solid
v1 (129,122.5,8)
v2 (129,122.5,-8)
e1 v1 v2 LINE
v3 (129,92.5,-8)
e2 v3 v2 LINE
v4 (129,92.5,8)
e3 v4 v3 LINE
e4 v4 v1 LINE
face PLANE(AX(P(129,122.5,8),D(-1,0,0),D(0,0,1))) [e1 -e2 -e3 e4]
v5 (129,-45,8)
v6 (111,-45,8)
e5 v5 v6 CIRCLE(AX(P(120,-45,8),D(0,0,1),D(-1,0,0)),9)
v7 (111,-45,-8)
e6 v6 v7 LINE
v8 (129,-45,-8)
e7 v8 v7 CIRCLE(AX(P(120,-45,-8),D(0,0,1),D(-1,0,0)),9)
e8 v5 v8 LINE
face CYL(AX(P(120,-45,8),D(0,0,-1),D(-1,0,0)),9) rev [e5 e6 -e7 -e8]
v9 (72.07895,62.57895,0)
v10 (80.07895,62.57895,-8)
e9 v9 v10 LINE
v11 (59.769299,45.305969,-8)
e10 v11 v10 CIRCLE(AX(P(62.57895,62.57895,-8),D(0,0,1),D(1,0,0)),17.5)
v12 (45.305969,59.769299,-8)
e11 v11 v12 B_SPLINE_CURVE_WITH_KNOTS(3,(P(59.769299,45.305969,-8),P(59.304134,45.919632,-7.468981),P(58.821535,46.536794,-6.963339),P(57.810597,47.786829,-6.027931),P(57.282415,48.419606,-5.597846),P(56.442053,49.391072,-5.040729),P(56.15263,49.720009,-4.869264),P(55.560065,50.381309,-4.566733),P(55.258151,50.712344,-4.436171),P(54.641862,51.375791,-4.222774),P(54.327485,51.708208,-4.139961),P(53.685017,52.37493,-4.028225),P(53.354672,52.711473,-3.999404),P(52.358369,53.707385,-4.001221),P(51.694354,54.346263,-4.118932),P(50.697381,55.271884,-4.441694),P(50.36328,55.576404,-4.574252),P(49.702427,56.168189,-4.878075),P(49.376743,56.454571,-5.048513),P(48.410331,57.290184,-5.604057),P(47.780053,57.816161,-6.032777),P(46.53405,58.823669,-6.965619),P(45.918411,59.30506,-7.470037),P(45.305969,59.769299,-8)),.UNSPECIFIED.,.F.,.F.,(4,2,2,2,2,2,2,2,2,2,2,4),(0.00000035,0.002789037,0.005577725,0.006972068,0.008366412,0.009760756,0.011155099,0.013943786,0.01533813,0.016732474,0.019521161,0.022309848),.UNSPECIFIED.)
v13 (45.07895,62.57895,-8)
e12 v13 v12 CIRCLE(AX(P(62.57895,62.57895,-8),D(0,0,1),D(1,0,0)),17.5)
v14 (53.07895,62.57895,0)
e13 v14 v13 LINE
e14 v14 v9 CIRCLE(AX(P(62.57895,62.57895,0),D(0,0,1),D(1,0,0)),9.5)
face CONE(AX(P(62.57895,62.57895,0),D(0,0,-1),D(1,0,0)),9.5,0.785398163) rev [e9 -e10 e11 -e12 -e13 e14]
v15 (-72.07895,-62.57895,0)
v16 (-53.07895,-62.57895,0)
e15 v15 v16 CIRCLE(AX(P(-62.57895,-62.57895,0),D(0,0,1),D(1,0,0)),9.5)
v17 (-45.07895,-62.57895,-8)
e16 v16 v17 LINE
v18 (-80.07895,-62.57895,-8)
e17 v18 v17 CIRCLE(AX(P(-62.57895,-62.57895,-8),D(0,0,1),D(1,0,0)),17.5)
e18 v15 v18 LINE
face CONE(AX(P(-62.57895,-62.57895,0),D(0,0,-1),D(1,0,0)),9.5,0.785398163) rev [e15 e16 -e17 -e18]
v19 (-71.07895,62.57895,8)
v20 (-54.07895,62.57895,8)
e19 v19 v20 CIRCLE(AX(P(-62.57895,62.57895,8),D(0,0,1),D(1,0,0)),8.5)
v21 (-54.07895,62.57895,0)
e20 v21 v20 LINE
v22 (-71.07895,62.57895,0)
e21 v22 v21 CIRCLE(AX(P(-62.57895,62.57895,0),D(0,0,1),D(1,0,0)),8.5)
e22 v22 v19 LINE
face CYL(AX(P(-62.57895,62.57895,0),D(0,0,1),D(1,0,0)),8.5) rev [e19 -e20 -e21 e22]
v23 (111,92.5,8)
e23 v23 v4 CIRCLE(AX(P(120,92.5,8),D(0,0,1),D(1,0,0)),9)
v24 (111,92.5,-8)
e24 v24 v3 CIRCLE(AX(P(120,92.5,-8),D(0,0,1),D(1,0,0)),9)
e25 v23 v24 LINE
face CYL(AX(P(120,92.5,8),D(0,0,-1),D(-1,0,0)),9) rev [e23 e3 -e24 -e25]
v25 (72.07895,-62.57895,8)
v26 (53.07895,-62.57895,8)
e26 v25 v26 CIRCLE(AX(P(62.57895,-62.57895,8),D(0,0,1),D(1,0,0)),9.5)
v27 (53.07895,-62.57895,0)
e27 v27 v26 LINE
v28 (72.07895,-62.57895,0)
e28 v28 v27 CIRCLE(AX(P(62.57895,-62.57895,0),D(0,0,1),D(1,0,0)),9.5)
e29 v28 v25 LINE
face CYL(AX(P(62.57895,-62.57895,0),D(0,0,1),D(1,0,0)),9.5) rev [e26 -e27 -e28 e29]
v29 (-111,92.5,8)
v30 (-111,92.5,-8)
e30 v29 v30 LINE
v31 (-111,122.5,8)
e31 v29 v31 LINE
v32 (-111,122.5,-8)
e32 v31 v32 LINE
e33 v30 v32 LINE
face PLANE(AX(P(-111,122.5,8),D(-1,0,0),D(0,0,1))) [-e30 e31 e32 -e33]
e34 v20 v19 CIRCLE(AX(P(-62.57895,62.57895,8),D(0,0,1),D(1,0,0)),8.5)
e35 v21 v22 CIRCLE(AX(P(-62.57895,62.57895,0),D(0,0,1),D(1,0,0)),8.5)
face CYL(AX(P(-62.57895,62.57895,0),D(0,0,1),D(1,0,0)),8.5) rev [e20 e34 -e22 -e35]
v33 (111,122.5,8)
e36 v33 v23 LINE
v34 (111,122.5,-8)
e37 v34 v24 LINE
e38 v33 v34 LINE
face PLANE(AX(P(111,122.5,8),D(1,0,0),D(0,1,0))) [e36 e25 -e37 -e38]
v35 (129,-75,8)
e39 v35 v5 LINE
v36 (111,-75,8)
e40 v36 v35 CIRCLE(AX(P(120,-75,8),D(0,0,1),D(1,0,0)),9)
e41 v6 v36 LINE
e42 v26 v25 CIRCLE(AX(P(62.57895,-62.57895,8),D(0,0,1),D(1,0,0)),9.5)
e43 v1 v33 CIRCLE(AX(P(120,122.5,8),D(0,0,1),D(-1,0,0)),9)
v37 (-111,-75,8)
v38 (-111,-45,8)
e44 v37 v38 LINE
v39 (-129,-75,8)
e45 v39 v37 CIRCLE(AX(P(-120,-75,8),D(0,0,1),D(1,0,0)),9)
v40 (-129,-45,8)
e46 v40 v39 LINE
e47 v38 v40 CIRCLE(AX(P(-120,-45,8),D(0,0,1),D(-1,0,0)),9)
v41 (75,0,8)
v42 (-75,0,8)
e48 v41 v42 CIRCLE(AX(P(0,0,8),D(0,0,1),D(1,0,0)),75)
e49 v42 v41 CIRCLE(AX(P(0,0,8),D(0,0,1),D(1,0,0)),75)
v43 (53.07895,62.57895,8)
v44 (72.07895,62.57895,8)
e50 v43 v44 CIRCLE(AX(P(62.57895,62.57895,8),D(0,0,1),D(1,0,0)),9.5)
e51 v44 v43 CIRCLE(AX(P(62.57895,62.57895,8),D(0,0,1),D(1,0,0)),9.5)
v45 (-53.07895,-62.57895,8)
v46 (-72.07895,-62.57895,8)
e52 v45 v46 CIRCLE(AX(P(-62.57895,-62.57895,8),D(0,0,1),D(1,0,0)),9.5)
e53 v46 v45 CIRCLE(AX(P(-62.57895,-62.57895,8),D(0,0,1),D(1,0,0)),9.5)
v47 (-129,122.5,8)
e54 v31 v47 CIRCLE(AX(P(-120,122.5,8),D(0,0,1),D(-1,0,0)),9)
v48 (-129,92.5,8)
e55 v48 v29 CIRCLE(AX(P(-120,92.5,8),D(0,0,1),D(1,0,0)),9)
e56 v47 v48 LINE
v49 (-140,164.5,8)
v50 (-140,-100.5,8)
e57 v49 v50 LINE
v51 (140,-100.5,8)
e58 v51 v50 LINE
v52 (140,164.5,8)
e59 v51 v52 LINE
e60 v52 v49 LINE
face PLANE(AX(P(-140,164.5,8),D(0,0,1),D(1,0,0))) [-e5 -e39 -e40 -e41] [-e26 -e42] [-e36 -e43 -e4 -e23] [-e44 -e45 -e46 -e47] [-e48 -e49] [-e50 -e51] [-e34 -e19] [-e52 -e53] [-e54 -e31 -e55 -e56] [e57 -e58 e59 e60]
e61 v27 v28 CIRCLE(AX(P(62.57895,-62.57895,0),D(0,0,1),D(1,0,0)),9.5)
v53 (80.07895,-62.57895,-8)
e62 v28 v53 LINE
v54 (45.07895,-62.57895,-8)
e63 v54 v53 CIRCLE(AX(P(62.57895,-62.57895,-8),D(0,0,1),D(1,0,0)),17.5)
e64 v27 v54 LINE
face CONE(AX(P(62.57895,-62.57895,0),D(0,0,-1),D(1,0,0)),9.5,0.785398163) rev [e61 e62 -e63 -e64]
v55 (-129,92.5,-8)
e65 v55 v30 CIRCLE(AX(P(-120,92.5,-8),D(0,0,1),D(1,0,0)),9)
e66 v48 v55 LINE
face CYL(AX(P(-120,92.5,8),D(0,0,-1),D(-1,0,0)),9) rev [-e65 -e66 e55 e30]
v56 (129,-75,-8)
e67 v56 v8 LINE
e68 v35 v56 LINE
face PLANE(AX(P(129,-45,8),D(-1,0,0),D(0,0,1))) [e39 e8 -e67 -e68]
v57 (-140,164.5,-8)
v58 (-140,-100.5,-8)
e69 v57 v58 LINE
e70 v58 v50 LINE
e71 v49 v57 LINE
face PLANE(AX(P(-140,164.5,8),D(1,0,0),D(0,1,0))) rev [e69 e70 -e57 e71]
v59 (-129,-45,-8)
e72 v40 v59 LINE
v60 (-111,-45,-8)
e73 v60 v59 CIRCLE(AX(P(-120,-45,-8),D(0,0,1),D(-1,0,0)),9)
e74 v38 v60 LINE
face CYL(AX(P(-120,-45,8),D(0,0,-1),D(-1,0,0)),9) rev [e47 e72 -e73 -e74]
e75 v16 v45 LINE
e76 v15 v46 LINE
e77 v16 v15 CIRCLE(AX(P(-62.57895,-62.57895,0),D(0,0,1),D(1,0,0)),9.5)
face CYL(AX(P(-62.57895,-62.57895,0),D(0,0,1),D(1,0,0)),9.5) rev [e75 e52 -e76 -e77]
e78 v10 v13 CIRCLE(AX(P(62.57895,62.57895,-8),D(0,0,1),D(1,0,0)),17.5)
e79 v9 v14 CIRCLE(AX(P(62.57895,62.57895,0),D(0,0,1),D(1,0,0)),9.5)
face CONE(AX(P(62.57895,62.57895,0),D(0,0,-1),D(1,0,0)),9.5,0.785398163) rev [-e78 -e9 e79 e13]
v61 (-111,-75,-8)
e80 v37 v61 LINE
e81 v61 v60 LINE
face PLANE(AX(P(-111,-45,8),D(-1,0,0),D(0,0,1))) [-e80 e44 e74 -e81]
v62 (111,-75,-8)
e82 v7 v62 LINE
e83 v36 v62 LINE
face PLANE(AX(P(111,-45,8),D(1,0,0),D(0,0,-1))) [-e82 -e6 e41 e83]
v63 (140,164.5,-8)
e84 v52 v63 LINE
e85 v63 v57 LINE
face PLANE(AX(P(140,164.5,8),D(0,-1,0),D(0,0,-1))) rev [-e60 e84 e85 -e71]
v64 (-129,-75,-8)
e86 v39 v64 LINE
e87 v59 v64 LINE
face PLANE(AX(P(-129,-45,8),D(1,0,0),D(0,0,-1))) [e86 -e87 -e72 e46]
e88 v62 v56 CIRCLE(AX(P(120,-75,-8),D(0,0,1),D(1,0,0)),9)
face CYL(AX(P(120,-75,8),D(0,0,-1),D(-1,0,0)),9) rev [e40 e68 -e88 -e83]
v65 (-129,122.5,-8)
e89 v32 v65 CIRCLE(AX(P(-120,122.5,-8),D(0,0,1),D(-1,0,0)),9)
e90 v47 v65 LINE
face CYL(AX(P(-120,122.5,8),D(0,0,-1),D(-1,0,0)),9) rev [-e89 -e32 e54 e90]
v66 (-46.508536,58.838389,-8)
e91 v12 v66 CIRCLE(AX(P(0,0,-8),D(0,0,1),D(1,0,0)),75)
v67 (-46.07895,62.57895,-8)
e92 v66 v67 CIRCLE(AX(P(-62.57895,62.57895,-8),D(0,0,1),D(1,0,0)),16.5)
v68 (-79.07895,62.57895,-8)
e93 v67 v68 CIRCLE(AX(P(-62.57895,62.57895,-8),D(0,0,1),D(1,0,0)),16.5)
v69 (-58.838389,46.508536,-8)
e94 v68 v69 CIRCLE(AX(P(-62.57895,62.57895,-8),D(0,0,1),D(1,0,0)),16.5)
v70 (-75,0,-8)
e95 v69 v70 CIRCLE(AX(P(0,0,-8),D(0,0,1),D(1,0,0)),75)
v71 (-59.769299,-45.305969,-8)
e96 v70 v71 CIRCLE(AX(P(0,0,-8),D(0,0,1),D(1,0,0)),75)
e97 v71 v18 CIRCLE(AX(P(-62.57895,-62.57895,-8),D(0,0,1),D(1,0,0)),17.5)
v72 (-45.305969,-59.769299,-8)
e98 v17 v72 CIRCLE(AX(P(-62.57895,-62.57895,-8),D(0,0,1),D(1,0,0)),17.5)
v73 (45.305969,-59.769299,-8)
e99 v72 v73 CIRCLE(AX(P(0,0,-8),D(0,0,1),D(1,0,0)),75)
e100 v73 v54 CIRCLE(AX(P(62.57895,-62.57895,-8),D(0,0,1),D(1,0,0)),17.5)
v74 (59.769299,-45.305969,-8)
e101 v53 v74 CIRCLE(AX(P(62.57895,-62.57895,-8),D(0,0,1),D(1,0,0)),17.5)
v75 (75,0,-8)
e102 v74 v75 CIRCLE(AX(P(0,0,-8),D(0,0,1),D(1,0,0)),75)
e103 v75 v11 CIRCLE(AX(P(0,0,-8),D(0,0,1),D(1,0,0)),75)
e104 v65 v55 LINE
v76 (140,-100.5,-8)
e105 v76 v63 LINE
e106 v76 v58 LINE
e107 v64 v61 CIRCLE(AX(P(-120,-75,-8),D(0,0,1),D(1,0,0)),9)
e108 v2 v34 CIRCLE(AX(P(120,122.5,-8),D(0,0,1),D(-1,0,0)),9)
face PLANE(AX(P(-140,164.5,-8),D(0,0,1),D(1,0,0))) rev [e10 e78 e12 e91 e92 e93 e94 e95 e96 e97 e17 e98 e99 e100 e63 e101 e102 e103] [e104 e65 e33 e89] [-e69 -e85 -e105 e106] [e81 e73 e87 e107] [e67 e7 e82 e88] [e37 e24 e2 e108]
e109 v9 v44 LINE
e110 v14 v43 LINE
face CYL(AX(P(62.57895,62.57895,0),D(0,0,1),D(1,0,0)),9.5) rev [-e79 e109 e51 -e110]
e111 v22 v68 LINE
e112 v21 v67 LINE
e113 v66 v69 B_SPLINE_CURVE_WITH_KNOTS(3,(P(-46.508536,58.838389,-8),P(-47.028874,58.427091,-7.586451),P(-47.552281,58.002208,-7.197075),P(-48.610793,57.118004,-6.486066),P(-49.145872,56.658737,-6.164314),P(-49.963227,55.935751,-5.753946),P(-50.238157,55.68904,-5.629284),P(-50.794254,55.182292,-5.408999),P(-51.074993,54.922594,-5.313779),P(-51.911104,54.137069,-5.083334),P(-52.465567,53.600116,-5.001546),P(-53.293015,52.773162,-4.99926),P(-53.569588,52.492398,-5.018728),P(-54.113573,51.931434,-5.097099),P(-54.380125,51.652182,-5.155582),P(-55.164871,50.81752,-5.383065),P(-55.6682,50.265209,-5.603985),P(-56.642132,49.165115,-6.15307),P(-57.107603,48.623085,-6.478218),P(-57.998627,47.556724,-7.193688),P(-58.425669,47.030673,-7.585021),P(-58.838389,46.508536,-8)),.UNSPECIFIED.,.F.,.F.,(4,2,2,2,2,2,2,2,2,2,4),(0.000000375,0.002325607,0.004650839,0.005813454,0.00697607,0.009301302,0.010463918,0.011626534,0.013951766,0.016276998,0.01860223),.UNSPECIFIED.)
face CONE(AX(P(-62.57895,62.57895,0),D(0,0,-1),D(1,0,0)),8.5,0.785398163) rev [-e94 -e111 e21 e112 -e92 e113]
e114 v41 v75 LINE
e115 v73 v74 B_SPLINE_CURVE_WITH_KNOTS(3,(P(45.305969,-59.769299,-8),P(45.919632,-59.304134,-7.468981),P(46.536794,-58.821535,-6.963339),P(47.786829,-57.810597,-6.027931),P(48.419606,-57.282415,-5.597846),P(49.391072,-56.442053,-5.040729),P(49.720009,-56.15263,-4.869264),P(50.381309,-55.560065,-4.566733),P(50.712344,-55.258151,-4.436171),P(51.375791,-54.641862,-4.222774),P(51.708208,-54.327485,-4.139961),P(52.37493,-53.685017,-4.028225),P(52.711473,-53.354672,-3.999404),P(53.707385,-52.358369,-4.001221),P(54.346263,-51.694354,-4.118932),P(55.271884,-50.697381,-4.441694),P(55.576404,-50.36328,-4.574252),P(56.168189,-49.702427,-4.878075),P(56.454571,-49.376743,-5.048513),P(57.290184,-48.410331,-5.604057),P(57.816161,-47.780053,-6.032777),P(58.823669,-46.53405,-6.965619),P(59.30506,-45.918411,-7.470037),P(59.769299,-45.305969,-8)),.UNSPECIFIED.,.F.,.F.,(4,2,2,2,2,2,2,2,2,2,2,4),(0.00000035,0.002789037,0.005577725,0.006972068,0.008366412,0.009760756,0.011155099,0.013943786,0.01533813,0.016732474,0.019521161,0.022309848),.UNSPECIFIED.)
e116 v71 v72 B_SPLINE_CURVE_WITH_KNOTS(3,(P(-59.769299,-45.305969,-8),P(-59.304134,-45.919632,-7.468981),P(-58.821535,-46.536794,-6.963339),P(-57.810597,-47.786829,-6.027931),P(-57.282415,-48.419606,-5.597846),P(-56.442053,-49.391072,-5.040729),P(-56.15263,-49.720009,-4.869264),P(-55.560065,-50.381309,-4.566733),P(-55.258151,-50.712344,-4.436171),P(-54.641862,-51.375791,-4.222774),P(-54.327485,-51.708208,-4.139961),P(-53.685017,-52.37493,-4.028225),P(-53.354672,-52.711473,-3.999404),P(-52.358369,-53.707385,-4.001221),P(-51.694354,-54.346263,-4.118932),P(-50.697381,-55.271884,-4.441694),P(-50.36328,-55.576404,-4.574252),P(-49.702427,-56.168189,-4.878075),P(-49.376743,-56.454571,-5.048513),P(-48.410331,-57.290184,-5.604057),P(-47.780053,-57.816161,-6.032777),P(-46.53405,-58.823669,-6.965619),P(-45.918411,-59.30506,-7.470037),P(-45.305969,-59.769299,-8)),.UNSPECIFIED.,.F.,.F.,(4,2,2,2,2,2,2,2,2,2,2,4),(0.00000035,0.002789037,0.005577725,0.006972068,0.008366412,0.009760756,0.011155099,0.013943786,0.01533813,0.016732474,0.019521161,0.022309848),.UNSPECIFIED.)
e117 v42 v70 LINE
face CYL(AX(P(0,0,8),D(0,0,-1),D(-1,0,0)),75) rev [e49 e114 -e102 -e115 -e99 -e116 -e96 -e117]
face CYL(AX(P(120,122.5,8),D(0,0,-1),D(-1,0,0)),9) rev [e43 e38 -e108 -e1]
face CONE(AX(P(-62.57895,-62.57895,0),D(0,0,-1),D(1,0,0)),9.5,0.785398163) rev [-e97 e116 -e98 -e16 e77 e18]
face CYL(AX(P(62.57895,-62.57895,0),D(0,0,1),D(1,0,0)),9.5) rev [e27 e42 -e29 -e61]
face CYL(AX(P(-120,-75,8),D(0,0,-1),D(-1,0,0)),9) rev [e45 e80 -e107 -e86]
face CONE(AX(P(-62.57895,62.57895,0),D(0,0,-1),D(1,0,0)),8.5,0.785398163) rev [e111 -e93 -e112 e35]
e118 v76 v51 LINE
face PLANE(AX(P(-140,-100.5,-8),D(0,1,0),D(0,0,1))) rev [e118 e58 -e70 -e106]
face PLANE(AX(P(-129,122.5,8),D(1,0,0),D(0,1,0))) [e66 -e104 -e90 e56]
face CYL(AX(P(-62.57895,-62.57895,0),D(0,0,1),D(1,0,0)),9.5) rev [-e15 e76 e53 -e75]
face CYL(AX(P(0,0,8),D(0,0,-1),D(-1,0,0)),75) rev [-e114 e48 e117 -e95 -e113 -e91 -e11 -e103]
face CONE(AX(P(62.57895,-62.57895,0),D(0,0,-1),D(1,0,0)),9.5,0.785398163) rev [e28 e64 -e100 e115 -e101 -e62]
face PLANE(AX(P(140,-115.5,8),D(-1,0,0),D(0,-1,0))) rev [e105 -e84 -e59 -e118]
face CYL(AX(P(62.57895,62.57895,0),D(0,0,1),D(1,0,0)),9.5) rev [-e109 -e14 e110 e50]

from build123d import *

# Parameters (mm, degrees)
SKETCH1_W                = 280
SKETCH1_H                = 280
SKETCH1_R                = 75
EXTRUDE1_DEPTH           = 8
SKETCH_2_2_R             = 8.5
SKETCH_2_2_R_2           = 9.5
EXTRUDE2_DEPTH           = 8
EXTRUDE4_START           = -8
SKETCH_2_2_2_R           = 8.5
EXTRUDE4_DEPTH           = 8
EXTRUDE4_DRAFT           = 45
SKETCH_2_2_2_R_2         = 9.5
EXTRUDE4_PROFILE_2_DEPTH = 8
EXTRUDE4_PROFILE_2_DRAFT = 45
EXTRUDE4_PROFILE_3_DEPTH = 8
EXTRUDE4_PROFILE_3_DRAFT = 45
EXTRUDE4_PROFILE_4_DEPTH = 8
EXTRUDE4_PROFILE_4_DRAFT = 45
SKETCH3_W                = 280
SKETCH3_H                = 15
EXTRUDE5_DEPTH           = 16


with BuildPart() as part:
    # Sketch1 → Extrude1 (new, symmetric)
    with BuildSketch(Plane.XY):
        with Locations((0, 24.5)):
            Rectangle(SKETCH1_W, SKETCH1_H)
        Circle(SKETCH1_R, mode=Mode.SUBTRACT)
        with BuildLine():
            Line((-129, 122.5), (-129, 92.5))
            ThreePointArc((-129, 92.5), (-120, 83.5), (-111, 92.5))
            Line((-111, 92.5), (-111, 122.5))
            ThreePointArc((-111, 122.5), (-120, 131.5), (-129, 122.5))
        make_face(mode=Mode.SUBTRACT)
        with BuildLine():
            Line((111, 122.5), (111, 92.5))
            ThreePointArc((111, 92.5), (120, 83.5), (129, 92.5))
            Line((129, 92.5), (129, 122.5))
            ThreePointArc((129, 122.5), (120, 131.5), (111, 122.5))
        make_face(mode=Mode.SUBTRACT)
        with BuildLine():
            Line((-129, -45), (-129, -75))
            ThreePointArc((-129, -75), (-120, -84), (-111, -75))
            Line((-111, -75), (-111, -45))
            ThreePointArc((-111, -45), (-120, -36), (-129, -45))
        make_face(mode=Mode.SUBTRACT)
        with BuildLine():
            Line((111, -45), (111, -75))
            ThreePointArc((111, -75), (120, -84), (129, -75))
            Line((129, -75), (129, -45))
            ThreePointArc((129, -45), (120, -36), (111, -45))
        make_face(mode=Mode.SUBTRACT)
    extrude(amount=EXTRUDE1_DEPTH, both=True)

    # Sketch 2_2 → Extrude2 (cut)
    with BuildSketch(Plane.XY.offset(8)):
        with Locations((-62.578950135, 62.578950135)):
            Circle(SKETCH_2_2_R)
        with Locations((62.578950135, 62.578950135)):
            Circle(SKETCH_2_2_R_2)
        with Locations((62.578950135, -62.578950135)):
            Circle(SKETCH_2_2_R_2)
        with Locations((-62.578950135, -62.578950135)):
            Circle(SKETCH_2_2_R_2)
    extrude(amount=-EXTRUDE2_DEPTH, mode=Mode.SUBTRACT)


with BuildPart() as extrude4_tool:
    # Sketch 2_2 2 → Extrude4 (with draft: the straight prism first)
    with BuildSketch(Plane.XY.offset(8).offset(EXTRUDE4_START)):
        with Locations((-62.578950135, 62.578950135)):
            Circle(SKETCH_2_2_2_R)
    extrude(amount=-EXTRUDE4_DEPTH)
    # Extrude4: the draft: its side faces are tilted about the plane it starts from
    extrude4_sides = [extrude4_tool.faces().sort_by_distance(p)[0] for p in [
        (-71.078950135, 62.578950135, -4),
    ]]
    draft(extrude4_sides, Plane.XY.offset(8).offset(EXTRUDE4_START), EXTRUDE4_DRAFT)


with BuildPart() as part_1:
    add(part.part)

    # Extrude4: cut by extrude4_tool
    add(extrude4_tool.part, mode=Mode.SUBTRACT)


with BuildPart() as extrude4_profile_2_tool:
    # Sketch 2_2 2 → Extrude4 profile 2 (with draft: the straight prism first)
    with BuildSketch(Plane.XY.offset(8).offset(EXTRUDE4_START)):
        with Locations((62.578950135, 62.578950135)):
            Circle(SKETCH_2_2_2_R_2)
    extrude(amount=-EXTRUDE4_PROFILE_2_DEPTH)
    # Extrude4 profile 2: the draft: its side faces are tilted about the plane it starts from
    extrude4_profile_2_sides = [extrude4_profile_2_tool.faces().sort_by_distance(p)[0] for p in [
        (53.078950135, 62.578950135, -4),
    ]]
    draft(extrude4_profile_2_sides, Plane.XY.offset(8).offset(EXTRUDE4_START), EXTRUDE4_PROFILE_2_DRAFT)


with BuildPart() as part_2:
    add(part_1.part)

    # Extrude4 profile 2: cut by extrude4_profile_2_tool
    add(extrude4_profile_2_tool.part, mode=Mode.SUBTRACT)


with BuildPart() as extrude4_profile_3_tool:
    # Sketch 2_2 2 → Extrude4 profile 3 (with draft: the straight prism first)
    with BuildSketch(Plane.XY.offset(8).offset(EXTRUDE4_START)):
        with Locations((62.578950135, -62.578950135)):
            Circle(SKETCH_2_2_2_R_2)
    extrude(amount=-EXTRUDE4_PROFILE_3_DEPTH)
    # Extrude4 profile 3: the draft: its side faces are tilted about the plane it starts from
    extrude4_profile_3_sides = [extrude4_profile_3_tool.faces().sort_by_distance(p)[0] for p in [
        (53.078950135, -62.578950135, -4),
    ]]
    draft(extrude4_profile_3_sides, Plane.XY.offset(8).offset(EXTRUDE4_START), EXTRUDE4_PROFILE_3_DRAFT)


with BuildPart() as part_3:
    add(part_2.part)

    # Extrude4 profile 3: cut by extrude4_profile_3_tool
    add(extrude4_profile_3_tool.part, mode=Mode.SUBTRACT)


with BuildPart() as extrude4_profile_4_tool:
    # Sketch 2_2 2 → Extrude4 profile 4 (with draft: the straight prism first)
    with BuildSketch(Plane.XY.offset(8).offset(EXTRUDE4_START)):
        with Locations((-62.578950135, -62.578950135)):
            Circle(SKETCH_2_2_2_R_2)
    extrude(amount=-EXTRUDE4_PROFILE_4_DEPTH)
    # Extrude4 profile 4: the draft: its side faces are tilted about the plane it starts from
    extrude4_profile_4_sides = [extrude4_profile_4_tool.faces().sort_by_distance(p)[0] for p in [
        (-72.078950135, -62.578950135, -4),
    ]]
    draft(extrude4_profile_4_sides, Plane.XY.offset(8).offset(EXTRUDE4_START), EXTRUDE4_PROFILE_4_DRAFT)


with BuildPart() as part_4:
    add(part_3.part)

    # Extrude4 profile 4: cut by extrude4_profile_4_tool
    add(extrude4_profile_4_tool.part, mode=Mode.SUBTRACT)

    # Sketch3 → Extrude5 (cut)
    with BuildSketch(Plane.XY.offset(8)):
        with Locations((0, -108)):
            Rectangle(SKETCH3_W, SKETCH3_H)
    extrude(amount=-EXTRUDE5_DEPTH, mode=Mode.SUBTRACT)


solid = part_4.part
